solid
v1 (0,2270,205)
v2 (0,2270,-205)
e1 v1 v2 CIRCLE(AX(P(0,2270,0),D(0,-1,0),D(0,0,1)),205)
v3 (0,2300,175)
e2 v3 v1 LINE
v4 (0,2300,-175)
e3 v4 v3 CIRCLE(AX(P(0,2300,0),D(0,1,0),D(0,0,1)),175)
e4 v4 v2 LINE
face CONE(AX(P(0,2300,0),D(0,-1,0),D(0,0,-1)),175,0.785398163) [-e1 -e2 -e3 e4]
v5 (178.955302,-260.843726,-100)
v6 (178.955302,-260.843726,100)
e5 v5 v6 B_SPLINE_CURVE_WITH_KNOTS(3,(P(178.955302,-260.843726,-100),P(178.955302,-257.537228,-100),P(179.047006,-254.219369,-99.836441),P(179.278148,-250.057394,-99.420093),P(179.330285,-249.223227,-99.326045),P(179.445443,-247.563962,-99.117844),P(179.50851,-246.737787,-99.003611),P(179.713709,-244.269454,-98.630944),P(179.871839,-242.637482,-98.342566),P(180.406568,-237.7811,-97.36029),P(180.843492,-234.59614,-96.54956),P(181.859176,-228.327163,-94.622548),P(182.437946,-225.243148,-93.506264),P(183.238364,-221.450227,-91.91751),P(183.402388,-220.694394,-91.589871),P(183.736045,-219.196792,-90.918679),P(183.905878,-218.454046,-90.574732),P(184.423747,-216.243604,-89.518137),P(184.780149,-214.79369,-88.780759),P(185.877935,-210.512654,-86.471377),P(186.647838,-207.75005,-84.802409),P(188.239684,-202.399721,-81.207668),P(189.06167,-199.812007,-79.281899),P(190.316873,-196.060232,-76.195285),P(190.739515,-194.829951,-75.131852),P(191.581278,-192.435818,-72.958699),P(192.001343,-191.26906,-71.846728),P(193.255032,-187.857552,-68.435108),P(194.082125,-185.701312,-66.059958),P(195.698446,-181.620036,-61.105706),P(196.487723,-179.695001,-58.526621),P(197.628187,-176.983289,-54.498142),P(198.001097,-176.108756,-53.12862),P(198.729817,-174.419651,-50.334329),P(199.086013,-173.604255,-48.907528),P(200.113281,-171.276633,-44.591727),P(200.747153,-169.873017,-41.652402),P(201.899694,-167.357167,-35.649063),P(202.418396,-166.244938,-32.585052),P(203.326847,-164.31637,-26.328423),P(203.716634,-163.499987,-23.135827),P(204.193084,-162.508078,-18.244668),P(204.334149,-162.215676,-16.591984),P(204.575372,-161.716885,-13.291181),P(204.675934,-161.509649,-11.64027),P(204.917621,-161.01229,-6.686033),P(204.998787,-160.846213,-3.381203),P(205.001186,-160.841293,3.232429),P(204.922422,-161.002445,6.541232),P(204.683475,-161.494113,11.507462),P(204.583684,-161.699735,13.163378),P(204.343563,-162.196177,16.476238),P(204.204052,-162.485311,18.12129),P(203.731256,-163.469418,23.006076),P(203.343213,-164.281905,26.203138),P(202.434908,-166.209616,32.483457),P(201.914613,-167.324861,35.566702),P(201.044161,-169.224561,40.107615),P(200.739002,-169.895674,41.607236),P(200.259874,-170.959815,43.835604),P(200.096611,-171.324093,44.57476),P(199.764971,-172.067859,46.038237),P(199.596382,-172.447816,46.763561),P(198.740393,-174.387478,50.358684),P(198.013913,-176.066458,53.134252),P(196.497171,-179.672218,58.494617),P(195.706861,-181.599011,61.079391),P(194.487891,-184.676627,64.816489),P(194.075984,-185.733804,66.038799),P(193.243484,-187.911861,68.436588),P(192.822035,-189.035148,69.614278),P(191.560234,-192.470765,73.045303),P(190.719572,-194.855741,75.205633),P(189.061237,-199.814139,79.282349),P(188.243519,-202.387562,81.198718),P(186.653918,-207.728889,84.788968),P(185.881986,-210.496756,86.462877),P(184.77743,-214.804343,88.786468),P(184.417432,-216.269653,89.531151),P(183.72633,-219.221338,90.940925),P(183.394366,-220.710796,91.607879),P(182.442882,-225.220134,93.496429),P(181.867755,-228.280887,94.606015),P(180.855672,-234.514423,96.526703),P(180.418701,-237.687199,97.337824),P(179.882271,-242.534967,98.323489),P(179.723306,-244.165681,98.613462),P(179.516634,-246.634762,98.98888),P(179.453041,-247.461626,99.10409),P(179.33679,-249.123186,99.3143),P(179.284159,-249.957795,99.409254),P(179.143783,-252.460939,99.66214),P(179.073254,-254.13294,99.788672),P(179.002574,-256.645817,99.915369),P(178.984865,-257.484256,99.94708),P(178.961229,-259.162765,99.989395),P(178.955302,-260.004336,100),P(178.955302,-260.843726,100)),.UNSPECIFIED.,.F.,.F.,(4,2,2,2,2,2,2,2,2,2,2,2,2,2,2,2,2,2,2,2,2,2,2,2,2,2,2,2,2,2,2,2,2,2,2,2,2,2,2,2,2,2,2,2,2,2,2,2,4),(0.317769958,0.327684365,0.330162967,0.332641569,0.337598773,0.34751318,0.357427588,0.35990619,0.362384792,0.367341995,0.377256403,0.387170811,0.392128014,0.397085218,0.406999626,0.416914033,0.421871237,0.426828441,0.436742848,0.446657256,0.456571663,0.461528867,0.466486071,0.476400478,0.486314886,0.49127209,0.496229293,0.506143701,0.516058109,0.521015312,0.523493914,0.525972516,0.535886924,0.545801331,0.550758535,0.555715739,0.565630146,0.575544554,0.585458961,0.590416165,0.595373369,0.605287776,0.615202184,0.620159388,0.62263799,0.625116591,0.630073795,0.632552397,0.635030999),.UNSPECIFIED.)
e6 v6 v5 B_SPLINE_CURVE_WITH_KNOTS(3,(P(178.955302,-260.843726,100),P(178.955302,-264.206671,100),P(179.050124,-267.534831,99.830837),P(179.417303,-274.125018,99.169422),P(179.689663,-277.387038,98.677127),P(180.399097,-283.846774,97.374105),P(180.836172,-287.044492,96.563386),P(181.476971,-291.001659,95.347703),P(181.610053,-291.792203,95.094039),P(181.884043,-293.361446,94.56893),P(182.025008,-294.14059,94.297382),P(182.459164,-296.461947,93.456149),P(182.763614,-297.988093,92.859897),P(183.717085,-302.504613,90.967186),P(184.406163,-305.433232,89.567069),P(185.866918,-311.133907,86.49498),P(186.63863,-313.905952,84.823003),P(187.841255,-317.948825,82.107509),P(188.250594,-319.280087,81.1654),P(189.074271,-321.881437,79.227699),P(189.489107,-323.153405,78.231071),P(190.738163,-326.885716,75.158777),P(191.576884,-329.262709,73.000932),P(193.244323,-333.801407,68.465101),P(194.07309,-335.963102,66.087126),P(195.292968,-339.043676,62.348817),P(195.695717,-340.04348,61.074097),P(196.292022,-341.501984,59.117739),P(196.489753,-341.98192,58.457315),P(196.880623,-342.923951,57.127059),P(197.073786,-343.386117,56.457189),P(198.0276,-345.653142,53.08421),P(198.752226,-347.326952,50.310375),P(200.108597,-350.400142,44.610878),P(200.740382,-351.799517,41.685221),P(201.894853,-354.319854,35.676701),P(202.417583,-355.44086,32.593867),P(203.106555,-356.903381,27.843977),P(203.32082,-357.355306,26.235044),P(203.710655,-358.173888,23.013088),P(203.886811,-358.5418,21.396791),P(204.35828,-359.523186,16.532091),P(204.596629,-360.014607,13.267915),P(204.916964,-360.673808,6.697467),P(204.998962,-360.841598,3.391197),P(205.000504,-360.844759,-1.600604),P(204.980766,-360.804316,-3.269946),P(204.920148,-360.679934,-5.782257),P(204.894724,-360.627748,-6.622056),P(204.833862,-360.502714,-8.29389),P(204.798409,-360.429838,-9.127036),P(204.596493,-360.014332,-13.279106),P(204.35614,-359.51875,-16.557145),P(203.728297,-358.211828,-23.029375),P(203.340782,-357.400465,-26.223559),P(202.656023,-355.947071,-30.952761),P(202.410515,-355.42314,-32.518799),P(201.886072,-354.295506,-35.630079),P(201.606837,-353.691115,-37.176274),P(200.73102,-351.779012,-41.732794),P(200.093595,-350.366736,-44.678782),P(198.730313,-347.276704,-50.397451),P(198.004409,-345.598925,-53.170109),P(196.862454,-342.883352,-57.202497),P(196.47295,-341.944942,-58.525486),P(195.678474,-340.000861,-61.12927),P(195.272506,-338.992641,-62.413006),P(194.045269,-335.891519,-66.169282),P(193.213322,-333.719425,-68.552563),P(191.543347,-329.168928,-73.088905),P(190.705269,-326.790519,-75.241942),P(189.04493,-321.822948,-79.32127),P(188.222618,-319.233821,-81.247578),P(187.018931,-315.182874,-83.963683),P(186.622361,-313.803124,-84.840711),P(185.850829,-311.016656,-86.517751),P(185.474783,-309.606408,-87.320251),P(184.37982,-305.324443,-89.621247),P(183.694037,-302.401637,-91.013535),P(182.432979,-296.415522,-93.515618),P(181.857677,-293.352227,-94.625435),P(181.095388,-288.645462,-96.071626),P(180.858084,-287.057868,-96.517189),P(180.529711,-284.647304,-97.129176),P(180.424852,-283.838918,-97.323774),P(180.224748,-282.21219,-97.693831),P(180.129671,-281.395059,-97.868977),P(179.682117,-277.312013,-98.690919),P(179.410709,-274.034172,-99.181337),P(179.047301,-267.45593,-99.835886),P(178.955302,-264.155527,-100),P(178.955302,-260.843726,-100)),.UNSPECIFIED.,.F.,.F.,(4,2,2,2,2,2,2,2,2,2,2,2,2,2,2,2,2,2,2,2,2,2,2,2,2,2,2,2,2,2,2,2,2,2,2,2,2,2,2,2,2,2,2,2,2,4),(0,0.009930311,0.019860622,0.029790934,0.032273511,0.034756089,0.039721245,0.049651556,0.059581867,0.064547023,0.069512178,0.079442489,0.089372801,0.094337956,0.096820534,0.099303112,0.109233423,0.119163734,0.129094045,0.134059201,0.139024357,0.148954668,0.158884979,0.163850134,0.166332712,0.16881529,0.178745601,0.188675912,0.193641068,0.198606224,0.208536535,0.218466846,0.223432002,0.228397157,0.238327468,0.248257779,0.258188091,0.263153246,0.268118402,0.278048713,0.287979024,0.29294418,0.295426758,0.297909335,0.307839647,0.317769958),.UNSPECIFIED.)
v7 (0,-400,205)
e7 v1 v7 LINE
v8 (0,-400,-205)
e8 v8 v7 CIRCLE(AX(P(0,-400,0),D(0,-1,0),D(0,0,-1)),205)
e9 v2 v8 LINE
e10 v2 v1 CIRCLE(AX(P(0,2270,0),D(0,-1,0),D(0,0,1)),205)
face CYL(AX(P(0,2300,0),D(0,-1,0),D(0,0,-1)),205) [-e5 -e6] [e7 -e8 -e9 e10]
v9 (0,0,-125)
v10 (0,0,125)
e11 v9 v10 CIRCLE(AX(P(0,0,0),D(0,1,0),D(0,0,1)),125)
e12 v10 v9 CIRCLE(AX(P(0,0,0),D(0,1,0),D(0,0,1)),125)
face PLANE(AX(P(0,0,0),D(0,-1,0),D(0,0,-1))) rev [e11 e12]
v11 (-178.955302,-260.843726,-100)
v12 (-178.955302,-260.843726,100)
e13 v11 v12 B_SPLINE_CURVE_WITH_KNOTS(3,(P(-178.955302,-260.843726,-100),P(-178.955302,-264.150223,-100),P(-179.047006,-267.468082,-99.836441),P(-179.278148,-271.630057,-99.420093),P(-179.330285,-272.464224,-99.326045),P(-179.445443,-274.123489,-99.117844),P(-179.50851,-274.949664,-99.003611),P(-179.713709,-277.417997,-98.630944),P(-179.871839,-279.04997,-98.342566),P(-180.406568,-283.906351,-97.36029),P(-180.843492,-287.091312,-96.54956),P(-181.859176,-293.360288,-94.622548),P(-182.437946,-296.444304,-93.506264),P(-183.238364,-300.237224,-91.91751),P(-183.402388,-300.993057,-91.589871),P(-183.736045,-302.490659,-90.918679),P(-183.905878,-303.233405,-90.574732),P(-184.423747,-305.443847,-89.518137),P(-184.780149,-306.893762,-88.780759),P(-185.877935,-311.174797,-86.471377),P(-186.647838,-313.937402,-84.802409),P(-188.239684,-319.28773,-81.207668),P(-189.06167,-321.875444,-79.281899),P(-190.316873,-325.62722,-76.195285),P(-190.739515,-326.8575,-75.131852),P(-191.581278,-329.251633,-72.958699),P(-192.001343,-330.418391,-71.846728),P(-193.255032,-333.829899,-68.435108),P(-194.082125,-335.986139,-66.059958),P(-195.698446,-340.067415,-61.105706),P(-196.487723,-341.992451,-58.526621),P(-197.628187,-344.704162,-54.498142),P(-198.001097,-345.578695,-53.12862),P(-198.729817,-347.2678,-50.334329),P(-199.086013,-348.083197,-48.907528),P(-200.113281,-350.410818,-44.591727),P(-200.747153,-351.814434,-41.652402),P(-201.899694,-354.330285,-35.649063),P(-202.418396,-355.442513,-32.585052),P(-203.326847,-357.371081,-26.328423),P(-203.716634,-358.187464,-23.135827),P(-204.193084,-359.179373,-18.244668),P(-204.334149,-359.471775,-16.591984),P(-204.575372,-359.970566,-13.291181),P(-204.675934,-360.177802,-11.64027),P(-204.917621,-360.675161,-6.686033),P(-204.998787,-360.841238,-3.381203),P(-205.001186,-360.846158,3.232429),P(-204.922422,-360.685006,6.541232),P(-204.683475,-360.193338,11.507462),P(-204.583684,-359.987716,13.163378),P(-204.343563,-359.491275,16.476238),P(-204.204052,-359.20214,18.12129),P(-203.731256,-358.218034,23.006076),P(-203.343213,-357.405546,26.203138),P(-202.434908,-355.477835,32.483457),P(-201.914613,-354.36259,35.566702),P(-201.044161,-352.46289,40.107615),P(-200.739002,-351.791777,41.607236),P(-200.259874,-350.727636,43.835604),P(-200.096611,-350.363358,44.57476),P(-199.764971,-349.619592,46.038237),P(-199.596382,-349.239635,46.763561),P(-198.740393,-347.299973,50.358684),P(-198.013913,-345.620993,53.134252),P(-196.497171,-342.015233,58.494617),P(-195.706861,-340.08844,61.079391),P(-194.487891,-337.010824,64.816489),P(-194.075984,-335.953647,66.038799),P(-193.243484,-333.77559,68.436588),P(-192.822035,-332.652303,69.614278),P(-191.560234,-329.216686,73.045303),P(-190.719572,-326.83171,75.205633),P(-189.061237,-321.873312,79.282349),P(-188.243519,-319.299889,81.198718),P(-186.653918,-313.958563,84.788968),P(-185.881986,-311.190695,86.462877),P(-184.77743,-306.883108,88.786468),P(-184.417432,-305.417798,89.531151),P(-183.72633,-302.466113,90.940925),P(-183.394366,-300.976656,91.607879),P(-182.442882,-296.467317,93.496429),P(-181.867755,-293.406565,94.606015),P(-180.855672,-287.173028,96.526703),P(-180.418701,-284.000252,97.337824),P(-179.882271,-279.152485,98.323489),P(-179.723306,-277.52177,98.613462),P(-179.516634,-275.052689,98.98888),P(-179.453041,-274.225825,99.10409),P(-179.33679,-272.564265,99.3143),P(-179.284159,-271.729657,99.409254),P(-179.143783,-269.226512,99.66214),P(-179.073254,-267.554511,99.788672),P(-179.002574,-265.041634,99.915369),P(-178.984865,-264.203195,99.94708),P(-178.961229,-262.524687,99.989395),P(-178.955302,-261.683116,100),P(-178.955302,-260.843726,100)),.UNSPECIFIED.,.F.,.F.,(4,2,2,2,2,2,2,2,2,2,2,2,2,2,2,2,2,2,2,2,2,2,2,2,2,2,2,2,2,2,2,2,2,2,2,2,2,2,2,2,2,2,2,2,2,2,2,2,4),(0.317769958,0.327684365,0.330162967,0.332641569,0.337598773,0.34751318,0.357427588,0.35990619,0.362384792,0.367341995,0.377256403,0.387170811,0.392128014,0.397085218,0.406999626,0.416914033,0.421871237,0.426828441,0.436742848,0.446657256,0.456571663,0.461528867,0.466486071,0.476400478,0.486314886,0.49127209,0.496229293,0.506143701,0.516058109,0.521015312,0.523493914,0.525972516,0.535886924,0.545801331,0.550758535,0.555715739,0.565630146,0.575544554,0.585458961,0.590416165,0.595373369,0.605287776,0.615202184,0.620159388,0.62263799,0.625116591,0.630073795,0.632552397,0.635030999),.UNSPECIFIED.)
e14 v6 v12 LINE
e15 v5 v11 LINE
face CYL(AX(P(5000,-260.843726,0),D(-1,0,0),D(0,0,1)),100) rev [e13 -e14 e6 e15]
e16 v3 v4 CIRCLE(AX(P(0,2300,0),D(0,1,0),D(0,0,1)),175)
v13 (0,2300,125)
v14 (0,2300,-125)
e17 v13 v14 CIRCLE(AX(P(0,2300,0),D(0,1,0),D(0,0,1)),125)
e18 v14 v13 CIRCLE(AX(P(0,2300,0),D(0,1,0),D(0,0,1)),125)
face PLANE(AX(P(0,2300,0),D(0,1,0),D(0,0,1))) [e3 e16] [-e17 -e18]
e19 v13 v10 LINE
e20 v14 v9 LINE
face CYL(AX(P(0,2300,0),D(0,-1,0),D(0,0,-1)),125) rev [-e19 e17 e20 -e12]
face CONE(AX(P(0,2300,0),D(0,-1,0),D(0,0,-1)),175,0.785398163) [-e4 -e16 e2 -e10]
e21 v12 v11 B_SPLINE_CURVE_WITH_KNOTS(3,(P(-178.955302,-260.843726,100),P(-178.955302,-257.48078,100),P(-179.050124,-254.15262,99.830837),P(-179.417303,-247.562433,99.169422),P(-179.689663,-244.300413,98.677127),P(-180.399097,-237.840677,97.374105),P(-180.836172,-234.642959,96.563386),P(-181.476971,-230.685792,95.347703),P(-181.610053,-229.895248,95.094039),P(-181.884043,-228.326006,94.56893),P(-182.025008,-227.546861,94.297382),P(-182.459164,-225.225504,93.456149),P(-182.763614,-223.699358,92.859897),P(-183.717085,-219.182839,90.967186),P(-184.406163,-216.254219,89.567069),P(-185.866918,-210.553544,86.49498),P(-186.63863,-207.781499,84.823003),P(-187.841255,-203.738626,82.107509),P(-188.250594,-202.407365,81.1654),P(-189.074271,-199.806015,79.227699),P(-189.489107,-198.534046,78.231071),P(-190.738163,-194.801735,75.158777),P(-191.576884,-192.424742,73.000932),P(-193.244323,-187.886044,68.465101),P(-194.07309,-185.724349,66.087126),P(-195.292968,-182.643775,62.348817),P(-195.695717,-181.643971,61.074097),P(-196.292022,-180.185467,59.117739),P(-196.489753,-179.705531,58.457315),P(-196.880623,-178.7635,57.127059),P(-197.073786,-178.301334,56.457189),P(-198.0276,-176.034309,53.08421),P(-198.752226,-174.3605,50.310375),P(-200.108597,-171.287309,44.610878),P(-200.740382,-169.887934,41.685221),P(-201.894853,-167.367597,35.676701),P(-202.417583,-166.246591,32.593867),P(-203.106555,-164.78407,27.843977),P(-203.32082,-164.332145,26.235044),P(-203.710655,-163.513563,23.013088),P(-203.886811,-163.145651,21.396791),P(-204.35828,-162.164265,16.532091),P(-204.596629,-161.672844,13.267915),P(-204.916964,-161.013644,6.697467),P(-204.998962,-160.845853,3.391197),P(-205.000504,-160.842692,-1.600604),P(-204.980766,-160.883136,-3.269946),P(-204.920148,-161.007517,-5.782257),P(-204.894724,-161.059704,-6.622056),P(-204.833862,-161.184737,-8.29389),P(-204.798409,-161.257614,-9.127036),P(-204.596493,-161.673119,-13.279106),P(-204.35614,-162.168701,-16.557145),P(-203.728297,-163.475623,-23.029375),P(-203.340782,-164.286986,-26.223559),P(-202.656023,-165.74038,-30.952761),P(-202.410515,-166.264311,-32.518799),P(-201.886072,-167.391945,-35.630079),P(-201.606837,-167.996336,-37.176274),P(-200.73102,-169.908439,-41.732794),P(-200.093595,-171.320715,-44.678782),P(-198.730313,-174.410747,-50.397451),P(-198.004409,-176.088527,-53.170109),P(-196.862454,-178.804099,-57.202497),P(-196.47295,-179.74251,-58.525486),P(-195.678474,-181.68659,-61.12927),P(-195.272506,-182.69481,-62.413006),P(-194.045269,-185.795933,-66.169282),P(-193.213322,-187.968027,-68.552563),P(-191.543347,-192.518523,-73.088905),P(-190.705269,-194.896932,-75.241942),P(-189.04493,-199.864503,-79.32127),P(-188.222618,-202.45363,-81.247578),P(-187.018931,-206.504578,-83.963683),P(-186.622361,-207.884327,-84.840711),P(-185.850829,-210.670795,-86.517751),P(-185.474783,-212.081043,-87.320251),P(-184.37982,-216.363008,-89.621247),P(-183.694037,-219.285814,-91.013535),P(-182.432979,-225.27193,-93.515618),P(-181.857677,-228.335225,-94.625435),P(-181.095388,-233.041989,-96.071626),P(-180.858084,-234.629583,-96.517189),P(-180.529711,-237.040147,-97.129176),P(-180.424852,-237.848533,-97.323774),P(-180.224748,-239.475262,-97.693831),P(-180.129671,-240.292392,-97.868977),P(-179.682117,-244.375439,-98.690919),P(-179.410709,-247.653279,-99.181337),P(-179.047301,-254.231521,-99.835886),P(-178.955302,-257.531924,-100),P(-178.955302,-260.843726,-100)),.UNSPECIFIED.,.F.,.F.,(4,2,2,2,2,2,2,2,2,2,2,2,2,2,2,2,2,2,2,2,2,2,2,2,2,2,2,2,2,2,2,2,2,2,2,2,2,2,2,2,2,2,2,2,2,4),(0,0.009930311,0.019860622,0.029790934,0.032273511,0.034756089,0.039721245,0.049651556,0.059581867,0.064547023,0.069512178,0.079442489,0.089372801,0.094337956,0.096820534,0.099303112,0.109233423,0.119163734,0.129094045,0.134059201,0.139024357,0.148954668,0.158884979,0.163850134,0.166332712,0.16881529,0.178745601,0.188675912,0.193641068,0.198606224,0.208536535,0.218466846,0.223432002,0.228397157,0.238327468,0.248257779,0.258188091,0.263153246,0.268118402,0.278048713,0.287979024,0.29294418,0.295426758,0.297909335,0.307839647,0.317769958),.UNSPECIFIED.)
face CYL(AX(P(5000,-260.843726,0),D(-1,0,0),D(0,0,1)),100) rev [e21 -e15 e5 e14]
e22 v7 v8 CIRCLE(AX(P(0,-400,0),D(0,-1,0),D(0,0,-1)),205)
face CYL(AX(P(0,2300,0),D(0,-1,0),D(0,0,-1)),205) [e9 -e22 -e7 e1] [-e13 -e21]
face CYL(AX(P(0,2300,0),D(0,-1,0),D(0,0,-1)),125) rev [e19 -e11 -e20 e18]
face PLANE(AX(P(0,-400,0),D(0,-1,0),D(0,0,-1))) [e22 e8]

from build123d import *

# Parameters (mm, degrees)
SKETCH1_R               = 205
SKETCH1_R_2             = 125
BOSS_EXTRUDE1_DEPTH     = 2300
BOSS_EXTRUDE2_START     = 400
SKETCH2_R               = 205
BOSS_EXTRUDE2_DEPTH     = 400
CUT_EXTRUDE1_DEPTH      = 5000
CUT_EXTRUDE1_DEPTH_BACK = 4000
SKETCH3_R               = 100
CHAMFER1_SIZE           = 30


with BuildPart() as part:
    # Sketch1 → Boss-Extrude1 (new body)
    with BuildSketch(Plane(origin=(0, 0, 0), x_dir=(1, 0, 0), z_dir=(0, 1, 0))):
        with Locations(Location((0, 0, 0), (0, 0, 270))):
            Circle(SKETCH1_R)
        with Locations(Location((0, 0, 0), (0, 0, 270))):
            Circle(SKETCH1_R_2, mode=Mode.SUBTRACT)
    extrude(amount=BOSS_EXTRUDE1_DEPTH)

    # Sketch2 → Boss-Extrude2 (add)
    with BuildSketch(Plane.XZ.offset(BOSS_EXTRUDE2_START)):
        with Locations(Location((0, 0, 0), (0, 0, 270))):
            Circle(SKETCH2_R)
    extrude(amount=-BOSS_EXTRUDE2_DEPTH)

    # Sketch3 → Cut-Extrude1 (cut, two sides: drawn at the far end of the back side and taken through both)
    with BuildSketch(Plane(origin=(0, 0, 0), x_dir=(0, 0, -1), z_dir=(1, 0, 0)).offset(-CUT_EXTRUDE1_DEPTH_BACK)):
        with Locations(Location((0, -260.843725605, 0), (0, 0, 180))):
            Circle(SKETCH3_R)
    extrude(amount=CUT_EXTRUDE1_DEPTH + CUT_EXTRUDE1_DEPTH_BACK, mode=Mode.SUBTRACT)

    # Chamfer1
    chamfer1_edges = [part.edges().sort_by_distance(p)[0] for p in [
        (0, 2300, -205),
    ]]
    chamfer(chamfer1_edges, length=CHAMFER1_SIZE)


solid = part.part
